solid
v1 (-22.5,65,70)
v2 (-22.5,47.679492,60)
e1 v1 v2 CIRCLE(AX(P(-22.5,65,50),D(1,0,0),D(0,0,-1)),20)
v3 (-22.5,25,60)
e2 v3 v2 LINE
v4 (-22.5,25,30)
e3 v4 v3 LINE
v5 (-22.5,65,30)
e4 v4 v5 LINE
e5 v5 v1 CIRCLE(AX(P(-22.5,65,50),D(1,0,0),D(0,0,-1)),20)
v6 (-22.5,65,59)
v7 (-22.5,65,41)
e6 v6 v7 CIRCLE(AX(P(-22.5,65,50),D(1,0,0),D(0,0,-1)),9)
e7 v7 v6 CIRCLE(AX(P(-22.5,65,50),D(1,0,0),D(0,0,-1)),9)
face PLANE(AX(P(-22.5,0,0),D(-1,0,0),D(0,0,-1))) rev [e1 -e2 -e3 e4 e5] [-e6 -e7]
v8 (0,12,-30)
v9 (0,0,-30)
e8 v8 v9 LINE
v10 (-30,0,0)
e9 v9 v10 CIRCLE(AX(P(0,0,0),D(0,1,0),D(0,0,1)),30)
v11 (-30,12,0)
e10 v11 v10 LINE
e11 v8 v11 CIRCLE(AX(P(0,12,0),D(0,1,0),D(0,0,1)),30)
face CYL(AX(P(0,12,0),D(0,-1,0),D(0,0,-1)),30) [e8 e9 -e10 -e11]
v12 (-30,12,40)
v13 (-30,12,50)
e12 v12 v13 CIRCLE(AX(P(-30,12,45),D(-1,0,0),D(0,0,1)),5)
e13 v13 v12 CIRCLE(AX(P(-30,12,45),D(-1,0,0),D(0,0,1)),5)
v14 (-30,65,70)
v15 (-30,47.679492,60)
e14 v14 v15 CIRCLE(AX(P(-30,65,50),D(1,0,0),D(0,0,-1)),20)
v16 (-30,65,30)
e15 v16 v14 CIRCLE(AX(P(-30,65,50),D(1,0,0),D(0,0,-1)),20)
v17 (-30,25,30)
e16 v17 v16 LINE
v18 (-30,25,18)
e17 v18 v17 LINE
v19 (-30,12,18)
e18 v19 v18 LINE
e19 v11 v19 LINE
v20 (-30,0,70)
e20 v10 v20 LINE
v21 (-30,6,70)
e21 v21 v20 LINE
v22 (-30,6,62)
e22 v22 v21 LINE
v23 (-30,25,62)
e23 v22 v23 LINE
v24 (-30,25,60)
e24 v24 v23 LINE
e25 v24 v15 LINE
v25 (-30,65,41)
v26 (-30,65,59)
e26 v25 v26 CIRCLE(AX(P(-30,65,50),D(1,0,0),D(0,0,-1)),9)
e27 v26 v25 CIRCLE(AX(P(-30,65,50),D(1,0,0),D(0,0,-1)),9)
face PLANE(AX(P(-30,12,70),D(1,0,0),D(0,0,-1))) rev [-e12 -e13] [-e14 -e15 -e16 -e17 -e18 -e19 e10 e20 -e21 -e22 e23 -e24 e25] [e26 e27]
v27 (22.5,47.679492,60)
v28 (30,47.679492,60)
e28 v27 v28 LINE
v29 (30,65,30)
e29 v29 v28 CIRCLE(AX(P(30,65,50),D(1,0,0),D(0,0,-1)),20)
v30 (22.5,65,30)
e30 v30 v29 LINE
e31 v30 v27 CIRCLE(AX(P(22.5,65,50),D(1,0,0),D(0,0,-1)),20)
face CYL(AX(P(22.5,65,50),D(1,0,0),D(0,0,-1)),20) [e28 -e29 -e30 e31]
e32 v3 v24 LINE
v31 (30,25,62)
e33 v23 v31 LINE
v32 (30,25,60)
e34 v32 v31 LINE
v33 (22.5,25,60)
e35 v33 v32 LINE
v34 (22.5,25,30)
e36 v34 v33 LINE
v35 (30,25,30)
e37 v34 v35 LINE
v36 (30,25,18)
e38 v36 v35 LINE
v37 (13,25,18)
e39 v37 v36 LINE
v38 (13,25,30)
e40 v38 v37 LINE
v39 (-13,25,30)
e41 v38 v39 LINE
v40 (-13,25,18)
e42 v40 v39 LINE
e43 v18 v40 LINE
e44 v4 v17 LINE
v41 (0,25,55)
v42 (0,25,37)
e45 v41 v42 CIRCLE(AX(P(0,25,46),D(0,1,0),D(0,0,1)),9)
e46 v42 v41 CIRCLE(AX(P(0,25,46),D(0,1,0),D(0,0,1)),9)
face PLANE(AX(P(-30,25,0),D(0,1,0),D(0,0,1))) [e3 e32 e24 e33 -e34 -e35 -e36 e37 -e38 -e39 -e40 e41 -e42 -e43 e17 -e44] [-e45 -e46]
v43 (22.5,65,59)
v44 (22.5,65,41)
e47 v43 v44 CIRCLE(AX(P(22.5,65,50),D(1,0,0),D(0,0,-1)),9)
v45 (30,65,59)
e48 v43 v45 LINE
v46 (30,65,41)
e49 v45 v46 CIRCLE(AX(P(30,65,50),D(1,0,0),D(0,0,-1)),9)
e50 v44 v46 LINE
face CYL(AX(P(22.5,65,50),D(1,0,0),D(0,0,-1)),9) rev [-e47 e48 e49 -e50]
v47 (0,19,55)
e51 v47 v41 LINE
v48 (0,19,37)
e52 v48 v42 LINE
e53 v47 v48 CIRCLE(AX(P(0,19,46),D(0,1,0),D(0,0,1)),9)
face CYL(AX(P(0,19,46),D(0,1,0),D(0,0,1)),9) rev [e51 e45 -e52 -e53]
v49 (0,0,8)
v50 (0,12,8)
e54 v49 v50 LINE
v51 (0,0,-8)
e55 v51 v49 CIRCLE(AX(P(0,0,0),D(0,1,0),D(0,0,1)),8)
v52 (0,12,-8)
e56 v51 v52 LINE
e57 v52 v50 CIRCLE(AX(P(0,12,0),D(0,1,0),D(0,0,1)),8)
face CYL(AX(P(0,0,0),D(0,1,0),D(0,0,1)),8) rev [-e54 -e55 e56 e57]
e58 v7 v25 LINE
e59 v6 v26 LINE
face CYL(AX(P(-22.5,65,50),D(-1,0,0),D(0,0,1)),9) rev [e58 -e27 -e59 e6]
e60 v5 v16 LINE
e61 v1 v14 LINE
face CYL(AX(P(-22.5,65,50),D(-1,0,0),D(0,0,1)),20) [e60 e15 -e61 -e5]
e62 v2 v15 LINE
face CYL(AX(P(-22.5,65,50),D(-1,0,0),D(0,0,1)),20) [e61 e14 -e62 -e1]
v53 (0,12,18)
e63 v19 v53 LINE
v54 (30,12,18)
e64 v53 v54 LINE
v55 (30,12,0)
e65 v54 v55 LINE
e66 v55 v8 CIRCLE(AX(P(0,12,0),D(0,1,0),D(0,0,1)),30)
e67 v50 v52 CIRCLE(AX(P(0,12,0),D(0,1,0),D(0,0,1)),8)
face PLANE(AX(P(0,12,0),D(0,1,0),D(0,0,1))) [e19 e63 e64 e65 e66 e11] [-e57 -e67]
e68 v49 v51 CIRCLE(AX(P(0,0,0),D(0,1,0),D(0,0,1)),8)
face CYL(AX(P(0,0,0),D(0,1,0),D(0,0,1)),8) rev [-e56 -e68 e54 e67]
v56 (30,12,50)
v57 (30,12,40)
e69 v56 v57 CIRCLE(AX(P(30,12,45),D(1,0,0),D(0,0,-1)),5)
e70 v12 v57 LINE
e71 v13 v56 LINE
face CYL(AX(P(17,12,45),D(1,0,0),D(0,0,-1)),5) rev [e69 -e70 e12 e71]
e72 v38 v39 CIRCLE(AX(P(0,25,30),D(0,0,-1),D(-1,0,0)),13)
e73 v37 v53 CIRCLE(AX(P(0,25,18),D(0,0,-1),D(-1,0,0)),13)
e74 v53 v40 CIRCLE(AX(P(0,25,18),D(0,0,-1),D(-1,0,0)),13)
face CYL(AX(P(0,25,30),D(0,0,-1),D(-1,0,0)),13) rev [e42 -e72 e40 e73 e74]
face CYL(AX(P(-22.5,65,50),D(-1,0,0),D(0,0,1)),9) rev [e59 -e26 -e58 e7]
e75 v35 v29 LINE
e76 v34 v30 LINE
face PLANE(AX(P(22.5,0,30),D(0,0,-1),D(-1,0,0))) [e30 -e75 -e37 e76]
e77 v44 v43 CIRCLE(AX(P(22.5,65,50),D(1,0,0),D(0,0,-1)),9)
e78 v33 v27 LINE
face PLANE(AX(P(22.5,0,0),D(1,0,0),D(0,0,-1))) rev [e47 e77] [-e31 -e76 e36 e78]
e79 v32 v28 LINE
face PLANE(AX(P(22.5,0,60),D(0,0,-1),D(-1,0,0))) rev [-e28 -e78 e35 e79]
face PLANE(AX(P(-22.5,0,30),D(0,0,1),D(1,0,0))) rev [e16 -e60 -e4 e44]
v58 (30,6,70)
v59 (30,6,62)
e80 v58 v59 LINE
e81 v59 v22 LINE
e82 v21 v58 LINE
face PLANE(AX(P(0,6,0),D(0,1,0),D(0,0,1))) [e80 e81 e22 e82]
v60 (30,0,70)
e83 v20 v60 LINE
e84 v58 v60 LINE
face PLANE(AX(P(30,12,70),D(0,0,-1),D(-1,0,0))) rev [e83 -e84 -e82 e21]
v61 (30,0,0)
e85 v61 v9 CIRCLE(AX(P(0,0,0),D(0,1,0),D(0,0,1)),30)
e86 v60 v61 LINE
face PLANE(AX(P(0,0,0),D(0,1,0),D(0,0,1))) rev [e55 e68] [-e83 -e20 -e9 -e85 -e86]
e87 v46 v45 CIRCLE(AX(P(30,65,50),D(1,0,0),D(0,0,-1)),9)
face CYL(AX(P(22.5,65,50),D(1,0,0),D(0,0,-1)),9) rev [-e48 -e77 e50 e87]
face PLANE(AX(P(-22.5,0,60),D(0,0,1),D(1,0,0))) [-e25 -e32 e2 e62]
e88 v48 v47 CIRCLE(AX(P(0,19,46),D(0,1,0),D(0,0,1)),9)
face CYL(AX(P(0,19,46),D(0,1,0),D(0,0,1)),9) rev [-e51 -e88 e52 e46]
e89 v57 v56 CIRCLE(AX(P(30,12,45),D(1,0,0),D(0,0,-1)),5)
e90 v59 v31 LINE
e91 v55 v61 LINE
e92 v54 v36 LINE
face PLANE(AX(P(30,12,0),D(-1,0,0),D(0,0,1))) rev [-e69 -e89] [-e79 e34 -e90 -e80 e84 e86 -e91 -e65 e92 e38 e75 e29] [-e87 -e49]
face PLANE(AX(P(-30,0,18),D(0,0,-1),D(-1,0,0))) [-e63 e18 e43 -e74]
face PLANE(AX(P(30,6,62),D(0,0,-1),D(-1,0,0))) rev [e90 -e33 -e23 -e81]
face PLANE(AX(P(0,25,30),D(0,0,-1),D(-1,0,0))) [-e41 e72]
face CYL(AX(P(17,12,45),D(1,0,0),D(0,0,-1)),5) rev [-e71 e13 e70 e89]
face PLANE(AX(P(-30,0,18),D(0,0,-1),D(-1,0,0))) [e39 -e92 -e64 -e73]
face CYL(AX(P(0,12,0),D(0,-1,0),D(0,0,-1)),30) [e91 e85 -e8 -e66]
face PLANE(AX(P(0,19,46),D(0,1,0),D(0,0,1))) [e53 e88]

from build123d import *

# Parameters (mm, degrees)
BASE_PLATE_DEPTH         = 12
CENTRE_HOLE_16_SKETCH_R  = 8
CENTRE_HOLE_16_DEPTH     = 12
GROOVE_SKETCH_W          = 60
GROOVE_SKETCH_H          = 8
GROOVE_8MM_DEPTH         = 6
UPRIGHT_WALL_DEPTH       = 60
PIN_LUG_SKETCH_R         = 9
PIN_LUG_DEPTH            = 7.5
HOLE_26_SKETCH_R         = 13
HOLE_26_DEPTH            = 12
RECESS_18_SKETCH_R       = 9
RECESS_18_DEPTH          = 6
SIDE_HOLE_10_SKETCH_R    = 5
SIDE_HOLE_10_DEPTH       = 13
LUG_START                = -85
LUG_PIN_HOLE_10_SKETCH_R = 5
LUG_PIN_HOLE_10_DEPTH    = 85


with BuildPart() as part:
    # Base Plate Sketch → Base Plate (new body)
    with BuildSketch(Plane(origin=(0, 0, 0), x_dir=(1, 0, 0), z_dir=(0, 1, 0))):
        with BuildLine():
            Line((30, 0), (30, -70))
            Line((30, -70), (-30, -70))
            Line((-30, -70), (-30, 0))
            ThreePointArc((-30, 0), (0, 30), (30, 0))
        make_face()
    extrude(amount=BASE_PLATE_DEPTH)

    # Centre Hole Ø16 Sketch → Centre Hole Ø16 (cut)
    with BuildSketch(Plane(origin=(0, 12, 0), x_dir=(1, 0, 0), z_dir=(0, 1, 0))):
        with Locations(Location((0, 0, 0), (0, 0, 270))):
            Circle(CENTRE_HOLE_16_SKETCH_R)
    extrude(amount=-CENTRE_HOLE_16_DEPTH, mode=Mode.SUBTRACT)

    # Groove Sketch → Groove 8mm (cut)
    with BuildSketch(Plane(origin=(0, 12, 0), x_dir=(1, 0, 0), z_dir=(0, 1, 0))):
        with Locations((0, -66)):
            Rectangle(GROOVE_SKETCH_W, GROOVE_SKETCH_H)
    extrude(amount=-GROOVE_8MM_DEPTH, mode=Mode.SUBTRACT)

    # Upright Wall Sketch → Upright Wall (add)
    with BuildSketch(Plane(origin=(30, 0, 0), x_dir=(0, 0, -1), z_dir=(1, 0, 0))):
        Polygon((-62, 12), (-18, 12), (-18, 25), (-30, 25), (-62, 25), align=None)
    extrude(amount=-UPRIGHT_WALL_DEPTH)

    # Pin Lug Sketch → Pin Lug (add)
    with BuildSketch(Plane(origin=(30, 0, 0), x_dir=(0, 0, -1), z_dir=(1, 0, 0))):
        with BuildLine():
            Line((-60, 25), (-30, 25))
            Line((-30, 25), (-30, 65))
            ThreePointArc((-30, 65), (-60, 82.320508076), (-60, 47.679491924))
            Line((-60, 47.679491924), (-60, 25))
        make_face()
        with Locations((-50, 65)):
            Circle(PIN_LUG_SKETCH_R, mode=Mode.SUBTRACT)
    pin_lug = extrude(amount=-PIN_LUG_DEPTH)

    # Pin Lug Mirror: Pin Lug across plane
    add(pin_lug.mirror(Plane(origin=(0, 0, 0), x_dir=(0, 0, 1), z_dir=(1, 0, 0))))

    # Hole Ø26 Sketch → Hole Ø26 (cut)
    with BuildSketch(Plane(origin=(0, 0, 18), x_dir=(-1, 0, 0), z_dir=(0, 0, -1))):
        with Locations((0, 25)):
            Circle(HOLE_26_SKETCH_R)
    extrude(amount=-HOLE_26_DEPTH, mode=Mode.SUBTRACT)

    # Recess Ø18 Sketch → Recess Ø18 (cut)
    with BuildSketch(Plane(origin=(0, 25, 0), x_dir=(1, 0, 0), z_dir=(0, 1, 0))):
        with Locations(Location((0, -46, 0), (0, 0, 270))):
            Circle(RECESS_18_SKETCH_R)
    extrude(amount=-RECESS_18_DEPTH, mode=Mode.SUBTRACT)

    # Side Hole Ø10 Sketch → Side Hole Ø10 (cut)
    with BuildSketch(Plane(origin=(30, 0, 0), x_dir=(0, 0, -1), z_dir=(1, 0, 0))):
        with Locations((-45, 12)):
            Circle(SIDE_HOLE_10_SKETCH_R)
    extrude(amount=-SIDE_HOLE_10_DEPTH, mode=Mode.SUBTRACT)

    # Lug Pin Hole Ø10 Sketch → Lug Pin Hole Ø10 (cut)
    with BuildSketch(Plane.ZY.offset(30).offset(LUG_START)):
        with Locations(Location((45, 12, 0), (0, 0, 180))):
            Circle(LUG_PIN_HOLE_10_SKETCH_R)
    extrude(amount=LUG_PIN_HOLE_10_DEPTH, mode=Mode.SUBTRACT)


solid = part.part
